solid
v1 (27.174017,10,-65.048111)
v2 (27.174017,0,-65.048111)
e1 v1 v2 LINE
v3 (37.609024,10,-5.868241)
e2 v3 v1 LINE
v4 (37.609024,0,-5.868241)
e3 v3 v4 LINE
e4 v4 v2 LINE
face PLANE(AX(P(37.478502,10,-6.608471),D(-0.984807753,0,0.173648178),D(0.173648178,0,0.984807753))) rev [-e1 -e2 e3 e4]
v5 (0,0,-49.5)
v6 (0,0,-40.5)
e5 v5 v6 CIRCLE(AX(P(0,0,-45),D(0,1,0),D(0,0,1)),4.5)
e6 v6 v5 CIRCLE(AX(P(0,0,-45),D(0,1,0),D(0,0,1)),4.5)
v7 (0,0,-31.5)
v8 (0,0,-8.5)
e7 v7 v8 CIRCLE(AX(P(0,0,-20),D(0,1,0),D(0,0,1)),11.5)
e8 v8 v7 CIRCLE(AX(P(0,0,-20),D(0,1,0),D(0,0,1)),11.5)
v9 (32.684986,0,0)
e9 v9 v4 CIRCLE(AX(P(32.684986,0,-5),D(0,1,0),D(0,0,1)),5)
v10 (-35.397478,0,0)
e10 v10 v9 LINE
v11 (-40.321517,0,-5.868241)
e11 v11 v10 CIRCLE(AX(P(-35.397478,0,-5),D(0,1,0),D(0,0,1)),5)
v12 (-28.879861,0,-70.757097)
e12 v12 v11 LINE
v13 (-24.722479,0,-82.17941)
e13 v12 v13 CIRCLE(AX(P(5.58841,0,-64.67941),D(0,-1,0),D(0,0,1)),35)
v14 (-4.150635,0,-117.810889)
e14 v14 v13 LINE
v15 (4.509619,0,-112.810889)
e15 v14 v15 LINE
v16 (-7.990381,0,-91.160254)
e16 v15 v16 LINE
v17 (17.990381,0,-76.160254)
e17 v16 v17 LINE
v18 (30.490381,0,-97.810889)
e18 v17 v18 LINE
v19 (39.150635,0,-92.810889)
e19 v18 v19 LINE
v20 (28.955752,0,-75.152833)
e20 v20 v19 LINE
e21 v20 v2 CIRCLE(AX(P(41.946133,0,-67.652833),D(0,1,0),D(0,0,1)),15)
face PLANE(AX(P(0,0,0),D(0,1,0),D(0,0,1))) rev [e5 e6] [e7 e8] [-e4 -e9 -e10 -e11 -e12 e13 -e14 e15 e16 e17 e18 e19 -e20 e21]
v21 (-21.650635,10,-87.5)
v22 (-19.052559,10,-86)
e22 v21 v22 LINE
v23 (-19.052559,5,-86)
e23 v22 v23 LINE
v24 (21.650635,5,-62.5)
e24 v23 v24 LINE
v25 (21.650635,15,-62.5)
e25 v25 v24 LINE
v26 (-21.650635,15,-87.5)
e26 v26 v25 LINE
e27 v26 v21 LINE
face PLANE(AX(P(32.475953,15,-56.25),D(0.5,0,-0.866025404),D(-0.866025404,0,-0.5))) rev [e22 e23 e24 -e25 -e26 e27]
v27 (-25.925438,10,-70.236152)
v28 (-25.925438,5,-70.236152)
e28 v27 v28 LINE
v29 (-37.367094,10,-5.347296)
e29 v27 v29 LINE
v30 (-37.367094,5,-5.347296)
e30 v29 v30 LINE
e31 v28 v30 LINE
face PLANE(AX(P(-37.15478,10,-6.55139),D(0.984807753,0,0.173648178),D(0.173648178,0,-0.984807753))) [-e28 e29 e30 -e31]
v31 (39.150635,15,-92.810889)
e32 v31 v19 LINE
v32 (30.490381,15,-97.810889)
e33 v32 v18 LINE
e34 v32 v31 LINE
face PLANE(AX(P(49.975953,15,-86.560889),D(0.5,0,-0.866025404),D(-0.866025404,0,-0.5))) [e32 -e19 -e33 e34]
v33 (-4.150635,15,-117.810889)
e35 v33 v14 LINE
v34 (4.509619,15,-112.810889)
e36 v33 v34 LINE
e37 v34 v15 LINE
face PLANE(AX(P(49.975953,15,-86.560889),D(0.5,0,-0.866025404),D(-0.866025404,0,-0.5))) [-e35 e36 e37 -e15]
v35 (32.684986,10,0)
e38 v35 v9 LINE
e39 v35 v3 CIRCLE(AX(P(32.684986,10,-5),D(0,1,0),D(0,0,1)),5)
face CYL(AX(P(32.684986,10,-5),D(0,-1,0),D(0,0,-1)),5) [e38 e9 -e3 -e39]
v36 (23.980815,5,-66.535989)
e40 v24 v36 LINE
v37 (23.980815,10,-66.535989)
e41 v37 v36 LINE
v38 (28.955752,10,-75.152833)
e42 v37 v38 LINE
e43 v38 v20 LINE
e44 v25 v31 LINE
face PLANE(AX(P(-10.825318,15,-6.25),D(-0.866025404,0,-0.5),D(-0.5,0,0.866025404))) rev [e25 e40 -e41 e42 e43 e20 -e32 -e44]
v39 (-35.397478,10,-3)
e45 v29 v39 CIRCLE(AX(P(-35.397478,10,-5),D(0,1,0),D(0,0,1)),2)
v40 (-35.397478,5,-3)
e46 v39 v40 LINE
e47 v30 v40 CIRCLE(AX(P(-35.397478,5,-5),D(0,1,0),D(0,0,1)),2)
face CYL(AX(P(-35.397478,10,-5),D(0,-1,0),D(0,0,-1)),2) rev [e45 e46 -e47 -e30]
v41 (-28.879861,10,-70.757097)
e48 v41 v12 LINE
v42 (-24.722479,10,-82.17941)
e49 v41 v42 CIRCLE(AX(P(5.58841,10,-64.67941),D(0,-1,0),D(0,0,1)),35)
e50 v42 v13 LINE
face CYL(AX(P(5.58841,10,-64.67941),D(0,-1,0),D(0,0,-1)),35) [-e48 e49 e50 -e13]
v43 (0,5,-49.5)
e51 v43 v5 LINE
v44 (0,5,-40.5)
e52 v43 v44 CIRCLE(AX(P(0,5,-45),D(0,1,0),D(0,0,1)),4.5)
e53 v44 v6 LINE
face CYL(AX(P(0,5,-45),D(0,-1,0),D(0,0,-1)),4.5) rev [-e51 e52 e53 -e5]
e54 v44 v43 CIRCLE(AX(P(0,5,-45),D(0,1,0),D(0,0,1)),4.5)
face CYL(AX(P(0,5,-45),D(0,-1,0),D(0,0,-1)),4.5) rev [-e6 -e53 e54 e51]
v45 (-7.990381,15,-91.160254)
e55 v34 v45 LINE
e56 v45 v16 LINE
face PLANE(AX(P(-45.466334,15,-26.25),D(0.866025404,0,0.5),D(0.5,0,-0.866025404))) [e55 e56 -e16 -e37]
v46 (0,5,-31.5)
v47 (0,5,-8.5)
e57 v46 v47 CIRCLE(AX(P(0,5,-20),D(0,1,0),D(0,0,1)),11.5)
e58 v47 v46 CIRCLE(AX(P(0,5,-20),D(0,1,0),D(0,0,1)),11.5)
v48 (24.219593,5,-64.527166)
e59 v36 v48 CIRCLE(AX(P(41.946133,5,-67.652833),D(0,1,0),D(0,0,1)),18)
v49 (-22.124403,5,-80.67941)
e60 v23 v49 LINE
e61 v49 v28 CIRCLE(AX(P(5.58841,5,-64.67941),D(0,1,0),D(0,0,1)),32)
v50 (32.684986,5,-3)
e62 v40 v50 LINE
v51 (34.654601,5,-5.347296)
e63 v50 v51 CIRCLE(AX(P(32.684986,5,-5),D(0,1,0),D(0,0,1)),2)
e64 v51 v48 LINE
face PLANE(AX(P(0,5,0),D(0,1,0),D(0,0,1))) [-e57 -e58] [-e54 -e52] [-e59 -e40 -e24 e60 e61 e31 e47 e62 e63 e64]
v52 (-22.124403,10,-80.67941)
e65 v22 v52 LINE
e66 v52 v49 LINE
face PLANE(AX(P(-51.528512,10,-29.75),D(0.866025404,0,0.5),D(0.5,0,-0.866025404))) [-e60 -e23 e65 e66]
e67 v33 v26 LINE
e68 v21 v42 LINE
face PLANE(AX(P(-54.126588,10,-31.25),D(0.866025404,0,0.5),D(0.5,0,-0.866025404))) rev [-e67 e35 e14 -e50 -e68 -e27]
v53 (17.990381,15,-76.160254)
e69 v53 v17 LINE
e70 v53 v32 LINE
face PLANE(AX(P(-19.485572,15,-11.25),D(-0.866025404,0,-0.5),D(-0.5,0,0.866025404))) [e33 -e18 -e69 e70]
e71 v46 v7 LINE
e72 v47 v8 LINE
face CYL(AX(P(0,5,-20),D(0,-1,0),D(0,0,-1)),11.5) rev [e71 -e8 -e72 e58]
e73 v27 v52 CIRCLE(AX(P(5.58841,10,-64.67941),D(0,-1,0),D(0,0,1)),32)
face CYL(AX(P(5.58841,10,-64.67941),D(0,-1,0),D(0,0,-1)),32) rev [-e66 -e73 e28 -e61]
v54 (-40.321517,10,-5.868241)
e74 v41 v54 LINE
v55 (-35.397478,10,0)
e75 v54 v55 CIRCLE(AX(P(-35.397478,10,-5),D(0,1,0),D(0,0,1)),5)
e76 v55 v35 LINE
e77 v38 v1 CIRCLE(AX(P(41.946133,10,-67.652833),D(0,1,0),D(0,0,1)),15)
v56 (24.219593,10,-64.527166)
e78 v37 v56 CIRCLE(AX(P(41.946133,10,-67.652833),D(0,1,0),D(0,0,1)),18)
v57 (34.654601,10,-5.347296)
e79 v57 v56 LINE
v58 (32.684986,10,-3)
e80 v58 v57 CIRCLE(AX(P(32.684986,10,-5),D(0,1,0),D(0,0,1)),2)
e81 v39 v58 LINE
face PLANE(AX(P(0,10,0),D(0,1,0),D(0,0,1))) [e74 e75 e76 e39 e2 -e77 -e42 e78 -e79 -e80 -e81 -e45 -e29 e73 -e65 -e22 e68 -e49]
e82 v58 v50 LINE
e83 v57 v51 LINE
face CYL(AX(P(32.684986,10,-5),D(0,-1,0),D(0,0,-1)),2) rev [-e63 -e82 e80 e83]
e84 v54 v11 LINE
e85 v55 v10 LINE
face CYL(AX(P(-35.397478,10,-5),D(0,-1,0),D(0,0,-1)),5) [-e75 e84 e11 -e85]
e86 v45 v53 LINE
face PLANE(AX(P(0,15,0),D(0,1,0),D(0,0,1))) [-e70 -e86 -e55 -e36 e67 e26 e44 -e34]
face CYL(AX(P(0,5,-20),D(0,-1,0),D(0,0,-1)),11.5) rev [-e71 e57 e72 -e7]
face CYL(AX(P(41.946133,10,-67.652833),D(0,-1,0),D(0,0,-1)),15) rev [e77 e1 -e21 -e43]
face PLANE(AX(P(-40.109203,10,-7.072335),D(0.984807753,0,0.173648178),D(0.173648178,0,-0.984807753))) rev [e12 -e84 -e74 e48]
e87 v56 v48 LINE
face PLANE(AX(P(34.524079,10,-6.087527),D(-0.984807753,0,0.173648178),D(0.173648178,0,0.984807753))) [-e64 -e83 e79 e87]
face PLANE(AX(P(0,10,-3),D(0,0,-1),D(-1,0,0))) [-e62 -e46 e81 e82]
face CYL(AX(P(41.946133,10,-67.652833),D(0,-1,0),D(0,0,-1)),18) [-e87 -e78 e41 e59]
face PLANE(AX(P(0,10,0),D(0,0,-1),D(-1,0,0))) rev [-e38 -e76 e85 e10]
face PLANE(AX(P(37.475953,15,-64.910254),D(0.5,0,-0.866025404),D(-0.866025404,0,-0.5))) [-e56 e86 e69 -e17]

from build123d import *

# Parameters (mm, degrees)
BASE_PLATE_DEPTH    = 10
RIM_WALL_SKETCH_R   = 11.5
RIM_WALL_SKETCH_R_2 = 4.5
RIM_WALL_DEPTH      = 5
FORK_BLOCK_DEPTH    = 15


with BuildPart() as part:
    # Base Plate Profile Sketch → Base Plate (new body)
    with BuildSketch(Plane(origin=(0, 0, 0), x_dir=(1, 0, 0), z_dir=(0, 1, 0))):
        with BuildLine():
            ThreePointArc((-24.722478982, 82.179410314), (-27.300831577, 76.65011533), (-28.879861205, 70.757096532))
            Line((-28.879861205, 70.757096532), (-40.321517202, 5.868240888))
            ThreePointArc((-40.321517202, 5.868240888), (-39.227700653, 1.786061952), (-35.397478437, 0))
            Line((-35.397478437, 0), (32.684985637, 0))
            ThreePointArc((32.684985637, 0), (36.515207852, 1.786061952), (37.609024402, 5.868240888))
            Line((37.609024402, 5.868240888), (27.174016631, 65.048110745))
            ThreePointArc((27.174016631, 65.048110745), (27.174016631, 70.257556075), (28.95575187, 75.15283341))
            Line((28.95575187, 75.15283341), (23.980814684, 66.53598944))
            ThreePointArc((23.980814684, 66.53598944), (24.071961031, 65.528220723), (24.219593372, 64.527166212))
            Line((24.219593372, 64.527166212), (34.654601143, 5.347296355))
            ThreePointArc((34.654601143, 5.347296355), (34.217074523, 3.714424781), (32.684985637, 3))
            Line((32.684985637, 3), (-35.397478437, 3))
            ThreePointArc((-35.397478437, 3), (-36.929567324, 3.714424781), (-37.367093943, 5.347296355))
            Line((-37.367093943, 5.347296355), (-25.925437946, 70.236151999))
            ThreePointArc((-25.925437946, 70.236151999), (-24.481753715, 75.6240549), (-22.124402771, 80.679410314))
            Line((-22.124402771, 80.679410314), (-19.052558883, 86))
            Line((-19.052558883, 86), (-21.650635095, 87.5))
            Line((-21.650635095, 87.5), (-24.722478982, 82.179410314))
        make_face()
    extrude(amount=BASE_PLATE_DEPTH)

    # Rim Wall Sketch → Rim Wall (add)
    with BuildSketch(Plane(origin=(0, 0, 0), x_dir=(1, 0, 0), z_dir=(0, 1, 0))):
        with BuildLine():
            Line((21.650635095, 62.5), (-19.052558883, 86))
            Line((-19.052558883, 86), (-22.124402771, 80.679410314))
            ThreePointArc((-22.124402771, 80.679410314), (-24.481753715, 75.6240549), (-25.925437946, 70.236151999))
            Line((-25.925437946, 70.236151999), (-37.367093943, 5.347296355))
            ThreePointArc((-37.367093943, 5.347296355), (-36.929567324, 3.714424781), (-35.397478437, 3))
            Line((-35.397478437, 3), (32.684985637, 3))
            ThreePointArc((32.684985637, 3), (34.217074523, 3.714424781), (34.654601143, 5.347296355))
            Line((34.654601143, 5.347296355), (24.219593372, 64.527166212))
            ThreePointArc((24.219593372, 64.527166212), (24.071961031, 65.528220723), (23.980814684, 66.53598944))
            Line((23.980814684, 66.53598944), (21.650635095, 62.5))
        make_face()
        with Locations(Location((0, 20, 0), (0, 0, 270))):
            Circle(RIM_WALL_SKETCH_R, mode=Mode.SUBTRACT)
        with Locations(Location((0, 45, 0), (0, 0, 270))):
            Circle(RIM_WALL_SKETCH_R_2, mode=Mode.SUBTRACT)
    extrude(amount=RIM_WALL_DEPTH)

    # Fork Block Sketch → Fork Block (add)
    with BuildSketch(Plane(origin=(0, 0, 0), x_dir=(1, 0, 0), z_dir=(0, 1, 0))):
        Polygon((39.150635095, 92.810889132), (30.490381057, 97.810889132), (17.990381057, 76.160254038), (-7.990381057, 91.160254038), (4.509618943, 112.810889132), (-4.150635095, 117.810889132), (-21.650635095, 87.5), (21.650635095, 62.5), align=None)
    extrude(amount=FORK_BLOCK_DEPTH)


solid = part.part
